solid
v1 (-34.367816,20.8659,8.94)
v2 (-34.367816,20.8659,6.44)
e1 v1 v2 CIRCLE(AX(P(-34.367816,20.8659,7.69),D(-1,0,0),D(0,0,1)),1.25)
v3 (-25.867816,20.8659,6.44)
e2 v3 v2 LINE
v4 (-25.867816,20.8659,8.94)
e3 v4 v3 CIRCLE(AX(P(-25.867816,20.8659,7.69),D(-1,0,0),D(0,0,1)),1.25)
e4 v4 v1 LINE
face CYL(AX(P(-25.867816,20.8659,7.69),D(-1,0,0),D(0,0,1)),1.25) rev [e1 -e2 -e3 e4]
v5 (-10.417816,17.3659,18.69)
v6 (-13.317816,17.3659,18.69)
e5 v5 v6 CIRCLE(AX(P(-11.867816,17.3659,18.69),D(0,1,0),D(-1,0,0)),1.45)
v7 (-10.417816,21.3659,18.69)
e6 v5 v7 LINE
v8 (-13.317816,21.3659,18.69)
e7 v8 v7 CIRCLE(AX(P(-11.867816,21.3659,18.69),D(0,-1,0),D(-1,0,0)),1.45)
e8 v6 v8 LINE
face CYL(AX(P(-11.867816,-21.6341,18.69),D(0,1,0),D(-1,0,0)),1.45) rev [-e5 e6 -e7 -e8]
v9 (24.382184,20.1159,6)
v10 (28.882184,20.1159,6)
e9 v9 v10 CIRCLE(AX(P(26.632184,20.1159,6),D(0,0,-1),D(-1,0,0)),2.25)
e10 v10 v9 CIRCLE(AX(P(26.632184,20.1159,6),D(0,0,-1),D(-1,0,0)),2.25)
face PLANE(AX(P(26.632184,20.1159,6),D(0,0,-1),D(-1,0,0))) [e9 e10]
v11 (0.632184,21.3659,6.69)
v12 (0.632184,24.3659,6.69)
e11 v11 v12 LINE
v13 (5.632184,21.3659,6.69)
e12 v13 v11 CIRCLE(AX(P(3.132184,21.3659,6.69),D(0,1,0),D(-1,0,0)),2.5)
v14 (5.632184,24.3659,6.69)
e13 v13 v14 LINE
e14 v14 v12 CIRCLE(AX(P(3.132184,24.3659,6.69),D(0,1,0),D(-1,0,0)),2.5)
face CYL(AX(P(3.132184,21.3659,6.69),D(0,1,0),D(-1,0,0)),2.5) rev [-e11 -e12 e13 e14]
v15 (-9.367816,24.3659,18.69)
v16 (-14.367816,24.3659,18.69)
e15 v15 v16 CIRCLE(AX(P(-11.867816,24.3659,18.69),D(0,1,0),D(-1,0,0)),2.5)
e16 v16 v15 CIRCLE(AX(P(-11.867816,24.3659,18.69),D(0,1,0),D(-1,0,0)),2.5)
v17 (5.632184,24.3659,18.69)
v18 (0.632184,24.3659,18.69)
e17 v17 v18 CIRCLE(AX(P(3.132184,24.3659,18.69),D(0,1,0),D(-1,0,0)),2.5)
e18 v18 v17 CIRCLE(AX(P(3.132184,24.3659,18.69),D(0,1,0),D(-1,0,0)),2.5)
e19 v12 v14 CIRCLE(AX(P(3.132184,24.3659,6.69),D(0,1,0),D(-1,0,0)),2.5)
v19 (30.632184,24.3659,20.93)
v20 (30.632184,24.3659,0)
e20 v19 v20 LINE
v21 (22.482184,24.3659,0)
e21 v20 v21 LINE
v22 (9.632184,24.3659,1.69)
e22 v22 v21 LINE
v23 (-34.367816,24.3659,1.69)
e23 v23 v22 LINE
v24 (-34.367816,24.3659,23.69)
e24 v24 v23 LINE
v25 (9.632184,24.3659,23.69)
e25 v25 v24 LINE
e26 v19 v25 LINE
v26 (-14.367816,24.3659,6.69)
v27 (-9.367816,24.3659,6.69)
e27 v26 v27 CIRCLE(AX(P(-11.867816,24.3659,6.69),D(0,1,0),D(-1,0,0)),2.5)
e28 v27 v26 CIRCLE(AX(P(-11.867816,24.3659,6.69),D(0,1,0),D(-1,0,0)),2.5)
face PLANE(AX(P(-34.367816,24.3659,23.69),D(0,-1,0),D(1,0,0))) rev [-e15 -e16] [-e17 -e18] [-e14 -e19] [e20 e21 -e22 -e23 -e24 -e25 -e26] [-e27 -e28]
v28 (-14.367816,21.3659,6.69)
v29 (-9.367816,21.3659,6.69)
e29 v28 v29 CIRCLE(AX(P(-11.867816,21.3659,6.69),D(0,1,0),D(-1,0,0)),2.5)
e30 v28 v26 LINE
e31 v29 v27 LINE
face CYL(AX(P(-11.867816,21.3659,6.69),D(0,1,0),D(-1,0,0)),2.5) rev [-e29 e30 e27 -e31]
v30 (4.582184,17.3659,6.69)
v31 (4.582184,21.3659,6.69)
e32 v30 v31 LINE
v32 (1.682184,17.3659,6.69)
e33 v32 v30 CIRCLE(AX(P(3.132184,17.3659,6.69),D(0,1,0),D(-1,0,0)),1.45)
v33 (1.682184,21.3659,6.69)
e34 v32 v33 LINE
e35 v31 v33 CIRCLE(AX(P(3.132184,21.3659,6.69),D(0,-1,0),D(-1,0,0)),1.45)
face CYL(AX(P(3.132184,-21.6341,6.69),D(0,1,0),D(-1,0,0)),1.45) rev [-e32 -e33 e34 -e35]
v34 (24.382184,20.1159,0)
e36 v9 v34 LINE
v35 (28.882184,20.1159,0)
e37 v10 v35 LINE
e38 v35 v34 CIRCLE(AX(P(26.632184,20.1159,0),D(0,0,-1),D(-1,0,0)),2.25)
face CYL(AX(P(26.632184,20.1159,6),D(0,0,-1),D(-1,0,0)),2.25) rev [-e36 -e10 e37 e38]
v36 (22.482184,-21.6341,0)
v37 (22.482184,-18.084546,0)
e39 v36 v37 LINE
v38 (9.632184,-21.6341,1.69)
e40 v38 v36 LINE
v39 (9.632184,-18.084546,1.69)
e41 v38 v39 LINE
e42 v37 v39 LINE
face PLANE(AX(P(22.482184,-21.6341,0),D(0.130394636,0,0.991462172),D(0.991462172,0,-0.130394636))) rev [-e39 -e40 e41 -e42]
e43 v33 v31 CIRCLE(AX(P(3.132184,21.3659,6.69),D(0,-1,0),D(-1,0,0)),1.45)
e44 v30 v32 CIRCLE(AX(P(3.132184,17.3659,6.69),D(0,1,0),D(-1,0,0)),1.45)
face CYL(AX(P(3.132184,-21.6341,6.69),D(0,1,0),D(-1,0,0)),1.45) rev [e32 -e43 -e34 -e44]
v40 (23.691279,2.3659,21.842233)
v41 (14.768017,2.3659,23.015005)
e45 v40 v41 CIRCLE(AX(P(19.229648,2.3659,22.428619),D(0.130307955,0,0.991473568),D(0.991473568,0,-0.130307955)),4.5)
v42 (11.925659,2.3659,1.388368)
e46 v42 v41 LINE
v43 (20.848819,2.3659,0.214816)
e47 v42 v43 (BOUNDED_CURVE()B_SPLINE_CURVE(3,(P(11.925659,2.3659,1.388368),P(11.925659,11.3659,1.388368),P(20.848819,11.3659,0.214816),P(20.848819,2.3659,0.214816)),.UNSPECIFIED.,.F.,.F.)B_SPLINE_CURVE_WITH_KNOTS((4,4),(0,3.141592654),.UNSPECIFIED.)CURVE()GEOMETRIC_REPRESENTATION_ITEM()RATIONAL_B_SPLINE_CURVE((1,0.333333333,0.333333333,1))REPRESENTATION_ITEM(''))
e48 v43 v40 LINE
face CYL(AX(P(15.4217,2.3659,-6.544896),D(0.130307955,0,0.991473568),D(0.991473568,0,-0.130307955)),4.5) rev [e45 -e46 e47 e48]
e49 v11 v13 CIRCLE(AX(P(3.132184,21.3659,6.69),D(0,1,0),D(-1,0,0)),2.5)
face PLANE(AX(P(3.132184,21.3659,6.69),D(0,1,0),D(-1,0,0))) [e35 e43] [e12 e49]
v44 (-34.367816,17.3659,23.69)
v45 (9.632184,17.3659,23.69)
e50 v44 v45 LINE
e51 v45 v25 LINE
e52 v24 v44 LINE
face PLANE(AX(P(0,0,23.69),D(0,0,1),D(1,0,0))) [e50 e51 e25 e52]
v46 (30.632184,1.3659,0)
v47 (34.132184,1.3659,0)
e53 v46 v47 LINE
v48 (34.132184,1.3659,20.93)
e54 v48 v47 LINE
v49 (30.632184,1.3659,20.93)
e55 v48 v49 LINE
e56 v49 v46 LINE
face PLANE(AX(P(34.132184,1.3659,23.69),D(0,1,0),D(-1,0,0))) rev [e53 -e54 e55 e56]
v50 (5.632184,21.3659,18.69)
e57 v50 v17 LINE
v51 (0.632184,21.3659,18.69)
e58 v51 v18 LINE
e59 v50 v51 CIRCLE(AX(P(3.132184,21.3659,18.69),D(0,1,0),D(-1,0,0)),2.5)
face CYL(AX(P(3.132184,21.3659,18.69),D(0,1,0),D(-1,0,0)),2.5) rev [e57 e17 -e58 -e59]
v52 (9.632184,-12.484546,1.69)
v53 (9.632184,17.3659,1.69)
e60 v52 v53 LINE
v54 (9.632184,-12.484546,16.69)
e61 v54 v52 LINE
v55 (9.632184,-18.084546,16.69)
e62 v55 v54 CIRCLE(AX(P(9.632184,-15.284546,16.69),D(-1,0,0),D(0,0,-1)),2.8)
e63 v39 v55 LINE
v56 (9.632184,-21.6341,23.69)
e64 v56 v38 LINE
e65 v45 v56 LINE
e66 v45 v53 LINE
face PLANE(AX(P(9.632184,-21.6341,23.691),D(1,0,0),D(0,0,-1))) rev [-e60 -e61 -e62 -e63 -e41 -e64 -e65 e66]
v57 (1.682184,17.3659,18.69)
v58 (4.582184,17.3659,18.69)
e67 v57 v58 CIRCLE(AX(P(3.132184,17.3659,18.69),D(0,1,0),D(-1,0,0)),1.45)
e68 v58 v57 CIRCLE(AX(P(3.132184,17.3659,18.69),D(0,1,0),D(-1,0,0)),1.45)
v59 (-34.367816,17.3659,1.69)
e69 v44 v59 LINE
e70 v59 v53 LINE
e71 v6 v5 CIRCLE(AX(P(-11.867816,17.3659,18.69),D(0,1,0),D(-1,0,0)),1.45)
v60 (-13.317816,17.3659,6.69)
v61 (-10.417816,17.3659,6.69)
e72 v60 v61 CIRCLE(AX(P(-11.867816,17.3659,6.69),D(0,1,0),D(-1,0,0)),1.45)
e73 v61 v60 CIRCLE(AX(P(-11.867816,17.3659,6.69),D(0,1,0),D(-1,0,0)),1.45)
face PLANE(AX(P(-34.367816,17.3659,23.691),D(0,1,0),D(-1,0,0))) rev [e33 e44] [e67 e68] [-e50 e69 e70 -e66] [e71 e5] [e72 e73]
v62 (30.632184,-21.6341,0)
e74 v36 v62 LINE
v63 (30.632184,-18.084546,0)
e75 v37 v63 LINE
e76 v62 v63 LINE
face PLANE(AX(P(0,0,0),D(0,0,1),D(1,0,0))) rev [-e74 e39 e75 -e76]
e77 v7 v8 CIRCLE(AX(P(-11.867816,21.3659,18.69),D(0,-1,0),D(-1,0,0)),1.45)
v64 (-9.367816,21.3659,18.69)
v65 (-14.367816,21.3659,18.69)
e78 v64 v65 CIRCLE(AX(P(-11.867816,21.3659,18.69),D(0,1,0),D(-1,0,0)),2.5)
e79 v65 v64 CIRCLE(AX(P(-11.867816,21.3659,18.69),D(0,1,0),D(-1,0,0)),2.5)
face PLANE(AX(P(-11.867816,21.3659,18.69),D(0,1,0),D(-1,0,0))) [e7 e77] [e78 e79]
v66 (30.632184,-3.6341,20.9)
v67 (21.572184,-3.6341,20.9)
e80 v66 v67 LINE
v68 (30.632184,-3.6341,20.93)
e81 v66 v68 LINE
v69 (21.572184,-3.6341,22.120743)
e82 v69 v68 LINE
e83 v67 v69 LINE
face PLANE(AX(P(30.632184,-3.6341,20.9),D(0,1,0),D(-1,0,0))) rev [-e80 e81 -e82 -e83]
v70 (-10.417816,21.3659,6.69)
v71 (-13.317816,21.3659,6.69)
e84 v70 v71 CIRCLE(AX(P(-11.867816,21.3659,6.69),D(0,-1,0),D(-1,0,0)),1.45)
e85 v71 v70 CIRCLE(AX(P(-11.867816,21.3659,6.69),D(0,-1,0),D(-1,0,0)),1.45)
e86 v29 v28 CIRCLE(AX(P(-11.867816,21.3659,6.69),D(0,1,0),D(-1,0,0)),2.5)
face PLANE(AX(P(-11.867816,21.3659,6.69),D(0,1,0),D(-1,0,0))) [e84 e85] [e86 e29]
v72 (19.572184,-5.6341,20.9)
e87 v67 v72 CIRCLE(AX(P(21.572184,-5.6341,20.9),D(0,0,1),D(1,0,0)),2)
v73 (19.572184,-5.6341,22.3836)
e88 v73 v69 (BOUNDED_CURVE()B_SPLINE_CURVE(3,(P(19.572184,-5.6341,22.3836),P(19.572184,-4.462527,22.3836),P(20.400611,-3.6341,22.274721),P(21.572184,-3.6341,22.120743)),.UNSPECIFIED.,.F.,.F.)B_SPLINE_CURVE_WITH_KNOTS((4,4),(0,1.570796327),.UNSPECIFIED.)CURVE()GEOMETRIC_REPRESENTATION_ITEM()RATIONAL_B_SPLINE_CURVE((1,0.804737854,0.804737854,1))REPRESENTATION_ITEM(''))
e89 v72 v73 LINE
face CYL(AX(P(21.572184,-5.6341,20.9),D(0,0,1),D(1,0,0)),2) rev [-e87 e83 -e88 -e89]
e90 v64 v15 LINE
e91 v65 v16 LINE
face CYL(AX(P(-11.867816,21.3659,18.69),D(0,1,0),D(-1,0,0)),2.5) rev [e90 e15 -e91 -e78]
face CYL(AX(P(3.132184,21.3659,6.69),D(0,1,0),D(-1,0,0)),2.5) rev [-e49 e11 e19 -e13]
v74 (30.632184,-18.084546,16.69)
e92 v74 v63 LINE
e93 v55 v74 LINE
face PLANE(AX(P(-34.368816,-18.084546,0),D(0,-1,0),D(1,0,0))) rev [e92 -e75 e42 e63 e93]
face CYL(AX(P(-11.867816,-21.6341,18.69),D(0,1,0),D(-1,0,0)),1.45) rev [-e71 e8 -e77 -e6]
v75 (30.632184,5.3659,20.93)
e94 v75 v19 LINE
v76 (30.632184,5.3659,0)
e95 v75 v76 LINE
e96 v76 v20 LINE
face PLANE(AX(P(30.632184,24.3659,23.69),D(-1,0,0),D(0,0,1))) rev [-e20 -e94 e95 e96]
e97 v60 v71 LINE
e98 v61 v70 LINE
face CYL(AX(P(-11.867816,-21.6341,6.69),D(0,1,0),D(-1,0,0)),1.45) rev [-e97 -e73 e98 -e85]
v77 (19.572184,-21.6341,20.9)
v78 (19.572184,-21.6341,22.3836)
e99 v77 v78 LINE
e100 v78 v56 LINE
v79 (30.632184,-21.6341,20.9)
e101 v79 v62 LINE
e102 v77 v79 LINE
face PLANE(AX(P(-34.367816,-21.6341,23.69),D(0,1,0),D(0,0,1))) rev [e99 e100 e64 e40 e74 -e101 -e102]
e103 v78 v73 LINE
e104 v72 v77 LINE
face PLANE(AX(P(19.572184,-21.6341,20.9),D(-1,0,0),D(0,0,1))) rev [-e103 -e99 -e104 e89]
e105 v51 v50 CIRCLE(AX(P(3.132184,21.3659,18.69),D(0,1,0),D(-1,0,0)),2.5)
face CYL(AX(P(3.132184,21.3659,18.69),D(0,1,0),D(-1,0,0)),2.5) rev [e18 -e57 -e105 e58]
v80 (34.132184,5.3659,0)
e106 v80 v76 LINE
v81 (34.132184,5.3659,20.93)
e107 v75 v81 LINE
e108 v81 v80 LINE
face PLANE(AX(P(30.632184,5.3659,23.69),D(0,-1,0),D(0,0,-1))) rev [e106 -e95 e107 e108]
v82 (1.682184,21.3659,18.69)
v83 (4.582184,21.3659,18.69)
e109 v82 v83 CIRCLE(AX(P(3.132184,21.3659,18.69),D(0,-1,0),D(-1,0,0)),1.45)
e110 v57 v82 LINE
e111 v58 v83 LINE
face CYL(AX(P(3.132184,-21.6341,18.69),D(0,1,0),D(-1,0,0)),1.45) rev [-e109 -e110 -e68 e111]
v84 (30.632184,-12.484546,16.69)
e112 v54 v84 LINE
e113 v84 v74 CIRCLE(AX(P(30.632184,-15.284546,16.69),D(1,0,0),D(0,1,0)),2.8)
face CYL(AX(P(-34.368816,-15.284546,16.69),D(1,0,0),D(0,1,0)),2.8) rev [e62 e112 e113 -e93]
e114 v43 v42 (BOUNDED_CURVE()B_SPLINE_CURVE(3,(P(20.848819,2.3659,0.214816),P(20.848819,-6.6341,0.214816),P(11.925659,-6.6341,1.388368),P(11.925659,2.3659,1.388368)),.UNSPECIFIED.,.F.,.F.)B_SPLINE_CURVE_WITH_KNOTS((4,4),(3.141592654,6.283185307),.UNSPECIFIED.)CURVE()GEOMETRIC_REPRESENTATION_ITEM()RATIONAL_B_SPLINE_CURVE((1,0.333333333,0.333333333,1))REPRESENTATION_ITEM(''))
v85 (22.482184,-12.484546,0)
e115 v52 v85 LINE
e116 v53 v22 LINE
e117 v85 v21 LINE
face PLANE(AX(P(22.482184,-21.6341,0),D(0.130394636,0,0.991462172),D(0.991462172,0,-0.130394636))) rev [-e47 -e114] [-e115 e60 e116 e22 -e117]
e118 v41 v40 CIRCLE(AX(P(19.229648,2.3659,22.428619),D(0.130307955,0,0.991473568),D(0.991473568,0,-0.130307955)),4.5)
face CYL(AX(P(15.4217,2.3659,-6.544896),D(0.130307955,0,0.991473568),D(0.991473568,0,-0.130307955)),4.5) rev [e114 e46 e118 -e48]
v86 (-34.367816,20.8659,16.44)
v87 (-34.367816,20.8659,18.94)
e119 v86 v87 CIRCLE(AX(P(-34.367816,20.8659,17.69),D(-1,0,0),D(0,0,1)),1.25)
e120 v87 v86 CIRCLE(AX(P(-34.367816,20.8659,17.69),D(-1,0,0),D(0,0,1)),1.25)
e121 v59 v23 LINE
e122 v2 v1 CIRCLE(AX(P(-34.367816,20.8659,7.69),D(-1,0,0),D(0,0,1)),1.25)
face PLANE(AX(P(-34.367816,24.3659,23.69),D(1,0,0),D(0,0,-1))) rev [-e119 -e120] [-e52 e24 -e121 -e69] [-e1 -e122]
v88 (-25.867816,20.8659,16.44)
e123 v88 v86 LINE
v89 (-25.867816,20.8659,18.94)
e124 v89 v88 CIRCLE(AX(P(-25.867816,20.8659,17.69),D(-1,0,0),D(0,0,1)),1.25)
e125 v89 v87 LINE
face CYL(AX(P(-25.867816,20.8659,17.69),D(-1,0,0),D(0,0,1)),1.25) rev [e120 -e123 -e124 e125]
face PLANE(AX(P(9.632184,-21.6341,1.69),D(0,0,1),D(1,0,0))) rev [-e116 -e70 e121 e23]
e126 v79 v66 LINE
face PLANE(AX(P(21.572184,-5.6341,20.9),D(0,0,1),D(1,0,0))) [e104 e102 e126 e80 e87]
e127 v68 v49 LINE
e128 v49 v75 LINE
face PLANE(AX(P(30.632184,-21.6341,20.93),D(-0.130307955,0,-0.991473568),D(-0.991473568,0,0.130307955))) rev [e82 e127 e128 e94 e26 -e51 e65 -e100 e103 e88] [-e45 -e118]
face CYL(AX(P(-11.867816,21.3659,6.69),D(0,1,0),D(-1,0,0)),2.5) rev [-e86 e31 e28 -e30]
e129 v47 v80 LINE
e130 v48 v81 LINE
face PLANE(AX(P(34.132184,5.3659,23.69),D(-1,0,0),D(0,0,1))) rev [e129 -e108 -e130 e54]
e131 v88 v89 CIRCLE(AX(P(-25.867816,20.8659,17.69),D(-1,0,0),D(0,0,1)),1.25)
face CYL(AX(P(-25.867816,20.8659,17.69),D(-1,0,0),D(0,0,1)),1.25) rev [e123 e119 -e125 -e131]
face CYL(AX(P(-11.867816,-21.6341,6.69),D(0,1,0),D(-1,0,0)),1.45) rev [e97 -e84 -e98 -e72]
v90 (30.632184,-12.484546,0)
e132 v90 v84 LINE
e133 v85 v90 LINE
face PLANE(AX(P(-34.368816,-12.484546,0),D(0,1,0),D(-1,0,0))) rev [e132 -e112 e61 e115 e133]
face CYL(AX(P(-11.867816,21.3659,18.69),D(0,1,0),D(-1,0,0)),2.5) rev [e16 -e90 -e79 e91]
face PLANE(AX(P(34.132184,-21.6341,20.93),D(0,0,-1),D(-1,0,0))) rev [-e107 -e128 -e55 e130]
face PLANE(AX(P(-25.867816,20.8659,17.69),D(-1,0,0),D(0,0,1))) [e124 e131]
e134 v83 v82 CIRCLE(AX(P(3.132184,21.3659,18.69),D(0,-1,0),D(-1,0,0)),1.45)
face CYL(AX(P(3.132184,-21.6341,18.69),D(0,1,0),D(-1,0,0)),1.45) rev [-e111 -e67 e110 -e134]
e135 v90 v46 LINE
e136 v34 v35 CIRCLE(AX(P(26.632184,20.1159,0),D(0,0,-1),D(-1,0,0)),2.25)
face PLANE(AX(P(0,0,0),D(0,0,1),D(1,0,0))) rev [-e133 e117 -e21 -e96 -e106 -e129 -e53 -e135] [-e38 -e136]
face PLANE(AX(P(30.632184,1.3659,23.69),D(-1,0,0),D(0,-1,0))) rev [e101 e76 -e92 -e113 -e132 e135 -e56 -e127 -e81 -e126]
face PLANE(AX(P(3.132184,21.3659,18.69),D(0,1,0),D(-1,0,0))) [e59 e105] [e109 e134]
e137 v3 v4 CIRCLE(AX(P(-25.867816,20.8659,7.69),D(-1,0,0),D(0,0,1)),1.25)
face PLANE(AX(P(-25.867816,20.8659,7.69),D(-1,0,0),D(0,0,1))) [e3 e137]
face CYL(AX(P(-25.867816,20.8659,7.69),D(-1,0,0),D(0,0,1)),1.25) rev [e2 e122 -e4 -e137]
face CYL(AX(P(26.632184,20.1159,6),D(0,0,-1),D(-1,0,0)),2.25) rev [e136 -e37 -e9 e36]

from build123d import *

# Parameters (mm, degrees)
EXTRUDE_1_DEPTH     = 23.69
CUT_EXTRUDE_1_REACH = 50.333
SKETCH_2_W          = 44
SKETCH_2_H          = 39
CUT_EXTRUDE_2_REACH = 75.348
CUT_EXTRUDE_3_DEPTH = 63.115721705
CUT_EXTRUDE_4_DEPTH = 2.79
CUT_EXTRUDE_5_REACH = 53.075
SKETCH_7_R          = 4.5
SKETCH_8_R          = 1.25
CUT_EXTRUDE_6_DEPTH = 8.5
SKETCH_10_R         = 1.45
CUT_EXTRUDE_7_DEPTH = 63.115721705
SKETCH_11_R         = 2.5
CUT_EXTRUDE_8_DEPTH = 3
SKETCH_12_R         = 2.25
CUT_EXTRUDE_9_DEPTH = 6


with BuildPart() as part:
    # 草图1 → 凸台-拉伸1 (new body)
    with BuildSketch(Plane.XY):
        Polygon((30.632183908, 5.365900383), (34.132183908, 5.365900383), (34.132183908, 1.365900383), (30.632183908, 1.365900383), (30.632183908, -21.634099617), (-34.367816092, -21.634099617), (-34.367816092, 24.365900383), (30.632183908, 24.365900383), align=None)
    extrude(amount=EXTRUDE_1_DEPTH)

    # 草图2 → 切除-拉伸1 (cut, up to next)
    with BuildSketch(Plane(origin=(0, 0, 0), x_dir=(-1, 0, 0), z_dir=(0, 0, -1)), mode=Mode.PRIVATE) as cut_extrude_1_sk1:
        with Locations((12.367816092, -2.134099617)):
            Rectangle(SKETCH_2_W, SKETCH_2_H)
    cut_extrude_1_tool1 = extrude(cut_extrude_1_sk1.sketch, amount=-CUT_EXTRUDE_1_REACH, mode=Mode.PRIVATE) & part.part
    add(cut_extrude_1_tool1.solids().sort_by_distance((-12.367816, -2.1341, 0))[0], mode=Mode.SUBTRACT)

    # 草图3 → 切除-拉伸2 (cut, up to next)
    with BuildSketch(Plane(origin=(30.632183908, 0, 0), x_dir=(0, 0, -1), z_dir=(1, 0, 0)), mode=Mode.PRIVATE) as cut_extrude_2_sk1:
        with BuildLine():
            Line((0, -18.084546462), (0, -12.484546462))
            Line((0, -12.484546462), (-16.69, -12.484546462))
            ThreePointArc((-16.69, -12.484546462), (-19.49, -15.284546462), (-16.69, -18.084546462))
            Line((-16.69, -18.084546462), (0, -18.084546462))
        make_face()
    cut_extrude_2_tool1 = extrude(cut_extrude_2_sk1.sketch, amount=-CUT_EXTRUDE_2_REACH, mode=Mode.PRIVATE) & part.part
    add(cut_extrude_2_tool1.solids().sort_by_distance((30.632184, -15.284546, 9.454896))[0], mode=Mode.SUBTRACT)

    # 草图4 → 切除-拉伸3 (cut, through all)
    with BuildSketch(Plane(origin=(0, 24.365900383, 0), x_dir=(1, 0, 0), z_dir=(0, 1, 0))):
        Polygon((9.632183908, -23.69), (34.132183908, -23.69), (34.132183908, -20.93), (30.632183908, -20.93), align=None)
        Polygon((-34.367816092, -1.69), (-34.367816092, 0), (22.482183908, 0), (9.632183908, -1.69), align=None)
    extrude(amount=-CUT_EXTRUDE_3_DEPTH, mode=Mode.SUBTRACT)

    # 草图5 → 切除-拉伸4 (cut)
    with BuildSketch(Plane.XY.offset(23.69)):
        with BuildLine():
            Line((30.632183908, -21.634099617), (19.572183908, -21.634099617))
            Line((19.572183908, -21.634099617), (19.572183908, -5.634099617))
            ThreePointArc((19.572183908, -5.634099617), (20.157970346, -4.219886054), (21.572183908, -3.634099617))
            Line((21.572183908, -3.634099617), (30.632183908, -3.634099617))
            Line((30.632183908, -3.634099617), (30.632183908, -21.634099617))
        make_face()
    extrude(amount=-CUT_EXTRUDE_4_DEPTH, mode=Mode.SUBTRACT)

    # 切除-拉伸5: up to this plane
    cut_extrude_5_end = Plane(origin=(22.482183908, -21.634099617, 0), z_dir=(0.13039463587890723, 0, 0.9914621722153636))
    # 草图7 → 切除-拉伸5 (cut, up to the surface)
    with BuildSketch(Plane(origin=(3.224230445, 0, 24.532188169), x_dir=(0.9914735684520677, 0, -0.1303079547108432), z_dir=(0.1303079547108432, 0, 0.9914735684520678)), mode=Mode.PRIVATE) as cut_extrude_5_sk1:
        with Locations((16.143060304, 2.365900383)):
            Circle(SKETCH_7_R)
    cut_extrude_5_tool1 = split(extrude(cut_extrude_5_sk1.sketch, amount=-CUT_EXTRUDE_5_REACH, mode=Mode.PRIVATE), bisect_by=cut_extrude_5_end, keep=Keep.BOTH, mode=Mode.PRIVATE)
    add(cut_extrude_5_tool1.solids().sort_by_distance((19.229648, 2.3659, 22.428619))[0], mode=Mode.SUBTRACT)

    # 草图8 → 切除-拉伸6 (cut)
    with BuildSketch(Plane.ZY.offset(34.367816092)):
        with Locations((7.69, 20.865900383)):
            Circle(SKETCH_8_R)
        with Locations((17.69, 20.865900383)):
            Circle(SKETCH_8_R)
    extrude(amount=-CUT_EXTRUDE_6_DEPTH, mode=Mode.SUBTRACT)

    # 草图10 → 切除-拉伸7 (cut, through all)
    with BuildSketch(Plane(origin=(0, 24.365900383, 0), x_dir=(1, 0, 0), z_dir=(0, 1, 0))):
        with Locations(Location((-11.867816092, -18.69, 0), (0, 0, 180))):
            Circle(SKETCH_10_R)
        with Locations(Location((-11.867816092, -6.69, 0), (0, 0, 180))):
            Circle(SKETCH_10_R)
        with Locations(Location((3.132183908, -18.69, 0), (0, 0, 180))):
            Circle(SKETCH_10_R)
        with Locations(Location((3.132183908, -6.69, 0), (0, 0, 180))):
            Circle(SKETCH_10_R)
    extrude(amount=-CUT_EXTRUDE_7_DEPTH, mode=Mode.SUBTRACT)

    # 草图11 → 切除-拉伸8 (cut)
    with BuildSketch(Plane(origin=(0, 24.365900383, 0), x_dir=(1, 0, 0), z_dir=(0, 1, 0))):
        with Locations(Location((-11.867816092, -6.69, 0), (0, 0, 180))):
            Circle(SKETCH_11_R)
        with Locations(Location((-11.867816092, -18.69, 0), (0, 0, 180))):
            Circle(SKETCH_11_R)
        with Locations(Location((3.132183908, -6.69, 0), (0, 0, 180))):
            Circle(SKETCH_11_R)
        with Locations(Location((3.132183908, -18.69, 0), (0, 0, 180))):
            Circle(SKETCH_11_R)
    extrude(amount=-CUT_EXTRUDE_8_DEPTH, mode=Mode.SUBTRACT)

    # 草图12 → 切除-拉伸9 (cut)
    with BuildSketch(Plane(origin=(0, 0, 0), x_dir=(-1, 0, 0), z_dir=(0, 0, -1))):
        with Locations((-26.632183908, 20.115900383)):
            Circle(SKETCH_12_R)
    extrude(amount=-CUT_EXTRUDE_9_DEPTH, mode=Mode.SUBTRACT)


solid = part.part
